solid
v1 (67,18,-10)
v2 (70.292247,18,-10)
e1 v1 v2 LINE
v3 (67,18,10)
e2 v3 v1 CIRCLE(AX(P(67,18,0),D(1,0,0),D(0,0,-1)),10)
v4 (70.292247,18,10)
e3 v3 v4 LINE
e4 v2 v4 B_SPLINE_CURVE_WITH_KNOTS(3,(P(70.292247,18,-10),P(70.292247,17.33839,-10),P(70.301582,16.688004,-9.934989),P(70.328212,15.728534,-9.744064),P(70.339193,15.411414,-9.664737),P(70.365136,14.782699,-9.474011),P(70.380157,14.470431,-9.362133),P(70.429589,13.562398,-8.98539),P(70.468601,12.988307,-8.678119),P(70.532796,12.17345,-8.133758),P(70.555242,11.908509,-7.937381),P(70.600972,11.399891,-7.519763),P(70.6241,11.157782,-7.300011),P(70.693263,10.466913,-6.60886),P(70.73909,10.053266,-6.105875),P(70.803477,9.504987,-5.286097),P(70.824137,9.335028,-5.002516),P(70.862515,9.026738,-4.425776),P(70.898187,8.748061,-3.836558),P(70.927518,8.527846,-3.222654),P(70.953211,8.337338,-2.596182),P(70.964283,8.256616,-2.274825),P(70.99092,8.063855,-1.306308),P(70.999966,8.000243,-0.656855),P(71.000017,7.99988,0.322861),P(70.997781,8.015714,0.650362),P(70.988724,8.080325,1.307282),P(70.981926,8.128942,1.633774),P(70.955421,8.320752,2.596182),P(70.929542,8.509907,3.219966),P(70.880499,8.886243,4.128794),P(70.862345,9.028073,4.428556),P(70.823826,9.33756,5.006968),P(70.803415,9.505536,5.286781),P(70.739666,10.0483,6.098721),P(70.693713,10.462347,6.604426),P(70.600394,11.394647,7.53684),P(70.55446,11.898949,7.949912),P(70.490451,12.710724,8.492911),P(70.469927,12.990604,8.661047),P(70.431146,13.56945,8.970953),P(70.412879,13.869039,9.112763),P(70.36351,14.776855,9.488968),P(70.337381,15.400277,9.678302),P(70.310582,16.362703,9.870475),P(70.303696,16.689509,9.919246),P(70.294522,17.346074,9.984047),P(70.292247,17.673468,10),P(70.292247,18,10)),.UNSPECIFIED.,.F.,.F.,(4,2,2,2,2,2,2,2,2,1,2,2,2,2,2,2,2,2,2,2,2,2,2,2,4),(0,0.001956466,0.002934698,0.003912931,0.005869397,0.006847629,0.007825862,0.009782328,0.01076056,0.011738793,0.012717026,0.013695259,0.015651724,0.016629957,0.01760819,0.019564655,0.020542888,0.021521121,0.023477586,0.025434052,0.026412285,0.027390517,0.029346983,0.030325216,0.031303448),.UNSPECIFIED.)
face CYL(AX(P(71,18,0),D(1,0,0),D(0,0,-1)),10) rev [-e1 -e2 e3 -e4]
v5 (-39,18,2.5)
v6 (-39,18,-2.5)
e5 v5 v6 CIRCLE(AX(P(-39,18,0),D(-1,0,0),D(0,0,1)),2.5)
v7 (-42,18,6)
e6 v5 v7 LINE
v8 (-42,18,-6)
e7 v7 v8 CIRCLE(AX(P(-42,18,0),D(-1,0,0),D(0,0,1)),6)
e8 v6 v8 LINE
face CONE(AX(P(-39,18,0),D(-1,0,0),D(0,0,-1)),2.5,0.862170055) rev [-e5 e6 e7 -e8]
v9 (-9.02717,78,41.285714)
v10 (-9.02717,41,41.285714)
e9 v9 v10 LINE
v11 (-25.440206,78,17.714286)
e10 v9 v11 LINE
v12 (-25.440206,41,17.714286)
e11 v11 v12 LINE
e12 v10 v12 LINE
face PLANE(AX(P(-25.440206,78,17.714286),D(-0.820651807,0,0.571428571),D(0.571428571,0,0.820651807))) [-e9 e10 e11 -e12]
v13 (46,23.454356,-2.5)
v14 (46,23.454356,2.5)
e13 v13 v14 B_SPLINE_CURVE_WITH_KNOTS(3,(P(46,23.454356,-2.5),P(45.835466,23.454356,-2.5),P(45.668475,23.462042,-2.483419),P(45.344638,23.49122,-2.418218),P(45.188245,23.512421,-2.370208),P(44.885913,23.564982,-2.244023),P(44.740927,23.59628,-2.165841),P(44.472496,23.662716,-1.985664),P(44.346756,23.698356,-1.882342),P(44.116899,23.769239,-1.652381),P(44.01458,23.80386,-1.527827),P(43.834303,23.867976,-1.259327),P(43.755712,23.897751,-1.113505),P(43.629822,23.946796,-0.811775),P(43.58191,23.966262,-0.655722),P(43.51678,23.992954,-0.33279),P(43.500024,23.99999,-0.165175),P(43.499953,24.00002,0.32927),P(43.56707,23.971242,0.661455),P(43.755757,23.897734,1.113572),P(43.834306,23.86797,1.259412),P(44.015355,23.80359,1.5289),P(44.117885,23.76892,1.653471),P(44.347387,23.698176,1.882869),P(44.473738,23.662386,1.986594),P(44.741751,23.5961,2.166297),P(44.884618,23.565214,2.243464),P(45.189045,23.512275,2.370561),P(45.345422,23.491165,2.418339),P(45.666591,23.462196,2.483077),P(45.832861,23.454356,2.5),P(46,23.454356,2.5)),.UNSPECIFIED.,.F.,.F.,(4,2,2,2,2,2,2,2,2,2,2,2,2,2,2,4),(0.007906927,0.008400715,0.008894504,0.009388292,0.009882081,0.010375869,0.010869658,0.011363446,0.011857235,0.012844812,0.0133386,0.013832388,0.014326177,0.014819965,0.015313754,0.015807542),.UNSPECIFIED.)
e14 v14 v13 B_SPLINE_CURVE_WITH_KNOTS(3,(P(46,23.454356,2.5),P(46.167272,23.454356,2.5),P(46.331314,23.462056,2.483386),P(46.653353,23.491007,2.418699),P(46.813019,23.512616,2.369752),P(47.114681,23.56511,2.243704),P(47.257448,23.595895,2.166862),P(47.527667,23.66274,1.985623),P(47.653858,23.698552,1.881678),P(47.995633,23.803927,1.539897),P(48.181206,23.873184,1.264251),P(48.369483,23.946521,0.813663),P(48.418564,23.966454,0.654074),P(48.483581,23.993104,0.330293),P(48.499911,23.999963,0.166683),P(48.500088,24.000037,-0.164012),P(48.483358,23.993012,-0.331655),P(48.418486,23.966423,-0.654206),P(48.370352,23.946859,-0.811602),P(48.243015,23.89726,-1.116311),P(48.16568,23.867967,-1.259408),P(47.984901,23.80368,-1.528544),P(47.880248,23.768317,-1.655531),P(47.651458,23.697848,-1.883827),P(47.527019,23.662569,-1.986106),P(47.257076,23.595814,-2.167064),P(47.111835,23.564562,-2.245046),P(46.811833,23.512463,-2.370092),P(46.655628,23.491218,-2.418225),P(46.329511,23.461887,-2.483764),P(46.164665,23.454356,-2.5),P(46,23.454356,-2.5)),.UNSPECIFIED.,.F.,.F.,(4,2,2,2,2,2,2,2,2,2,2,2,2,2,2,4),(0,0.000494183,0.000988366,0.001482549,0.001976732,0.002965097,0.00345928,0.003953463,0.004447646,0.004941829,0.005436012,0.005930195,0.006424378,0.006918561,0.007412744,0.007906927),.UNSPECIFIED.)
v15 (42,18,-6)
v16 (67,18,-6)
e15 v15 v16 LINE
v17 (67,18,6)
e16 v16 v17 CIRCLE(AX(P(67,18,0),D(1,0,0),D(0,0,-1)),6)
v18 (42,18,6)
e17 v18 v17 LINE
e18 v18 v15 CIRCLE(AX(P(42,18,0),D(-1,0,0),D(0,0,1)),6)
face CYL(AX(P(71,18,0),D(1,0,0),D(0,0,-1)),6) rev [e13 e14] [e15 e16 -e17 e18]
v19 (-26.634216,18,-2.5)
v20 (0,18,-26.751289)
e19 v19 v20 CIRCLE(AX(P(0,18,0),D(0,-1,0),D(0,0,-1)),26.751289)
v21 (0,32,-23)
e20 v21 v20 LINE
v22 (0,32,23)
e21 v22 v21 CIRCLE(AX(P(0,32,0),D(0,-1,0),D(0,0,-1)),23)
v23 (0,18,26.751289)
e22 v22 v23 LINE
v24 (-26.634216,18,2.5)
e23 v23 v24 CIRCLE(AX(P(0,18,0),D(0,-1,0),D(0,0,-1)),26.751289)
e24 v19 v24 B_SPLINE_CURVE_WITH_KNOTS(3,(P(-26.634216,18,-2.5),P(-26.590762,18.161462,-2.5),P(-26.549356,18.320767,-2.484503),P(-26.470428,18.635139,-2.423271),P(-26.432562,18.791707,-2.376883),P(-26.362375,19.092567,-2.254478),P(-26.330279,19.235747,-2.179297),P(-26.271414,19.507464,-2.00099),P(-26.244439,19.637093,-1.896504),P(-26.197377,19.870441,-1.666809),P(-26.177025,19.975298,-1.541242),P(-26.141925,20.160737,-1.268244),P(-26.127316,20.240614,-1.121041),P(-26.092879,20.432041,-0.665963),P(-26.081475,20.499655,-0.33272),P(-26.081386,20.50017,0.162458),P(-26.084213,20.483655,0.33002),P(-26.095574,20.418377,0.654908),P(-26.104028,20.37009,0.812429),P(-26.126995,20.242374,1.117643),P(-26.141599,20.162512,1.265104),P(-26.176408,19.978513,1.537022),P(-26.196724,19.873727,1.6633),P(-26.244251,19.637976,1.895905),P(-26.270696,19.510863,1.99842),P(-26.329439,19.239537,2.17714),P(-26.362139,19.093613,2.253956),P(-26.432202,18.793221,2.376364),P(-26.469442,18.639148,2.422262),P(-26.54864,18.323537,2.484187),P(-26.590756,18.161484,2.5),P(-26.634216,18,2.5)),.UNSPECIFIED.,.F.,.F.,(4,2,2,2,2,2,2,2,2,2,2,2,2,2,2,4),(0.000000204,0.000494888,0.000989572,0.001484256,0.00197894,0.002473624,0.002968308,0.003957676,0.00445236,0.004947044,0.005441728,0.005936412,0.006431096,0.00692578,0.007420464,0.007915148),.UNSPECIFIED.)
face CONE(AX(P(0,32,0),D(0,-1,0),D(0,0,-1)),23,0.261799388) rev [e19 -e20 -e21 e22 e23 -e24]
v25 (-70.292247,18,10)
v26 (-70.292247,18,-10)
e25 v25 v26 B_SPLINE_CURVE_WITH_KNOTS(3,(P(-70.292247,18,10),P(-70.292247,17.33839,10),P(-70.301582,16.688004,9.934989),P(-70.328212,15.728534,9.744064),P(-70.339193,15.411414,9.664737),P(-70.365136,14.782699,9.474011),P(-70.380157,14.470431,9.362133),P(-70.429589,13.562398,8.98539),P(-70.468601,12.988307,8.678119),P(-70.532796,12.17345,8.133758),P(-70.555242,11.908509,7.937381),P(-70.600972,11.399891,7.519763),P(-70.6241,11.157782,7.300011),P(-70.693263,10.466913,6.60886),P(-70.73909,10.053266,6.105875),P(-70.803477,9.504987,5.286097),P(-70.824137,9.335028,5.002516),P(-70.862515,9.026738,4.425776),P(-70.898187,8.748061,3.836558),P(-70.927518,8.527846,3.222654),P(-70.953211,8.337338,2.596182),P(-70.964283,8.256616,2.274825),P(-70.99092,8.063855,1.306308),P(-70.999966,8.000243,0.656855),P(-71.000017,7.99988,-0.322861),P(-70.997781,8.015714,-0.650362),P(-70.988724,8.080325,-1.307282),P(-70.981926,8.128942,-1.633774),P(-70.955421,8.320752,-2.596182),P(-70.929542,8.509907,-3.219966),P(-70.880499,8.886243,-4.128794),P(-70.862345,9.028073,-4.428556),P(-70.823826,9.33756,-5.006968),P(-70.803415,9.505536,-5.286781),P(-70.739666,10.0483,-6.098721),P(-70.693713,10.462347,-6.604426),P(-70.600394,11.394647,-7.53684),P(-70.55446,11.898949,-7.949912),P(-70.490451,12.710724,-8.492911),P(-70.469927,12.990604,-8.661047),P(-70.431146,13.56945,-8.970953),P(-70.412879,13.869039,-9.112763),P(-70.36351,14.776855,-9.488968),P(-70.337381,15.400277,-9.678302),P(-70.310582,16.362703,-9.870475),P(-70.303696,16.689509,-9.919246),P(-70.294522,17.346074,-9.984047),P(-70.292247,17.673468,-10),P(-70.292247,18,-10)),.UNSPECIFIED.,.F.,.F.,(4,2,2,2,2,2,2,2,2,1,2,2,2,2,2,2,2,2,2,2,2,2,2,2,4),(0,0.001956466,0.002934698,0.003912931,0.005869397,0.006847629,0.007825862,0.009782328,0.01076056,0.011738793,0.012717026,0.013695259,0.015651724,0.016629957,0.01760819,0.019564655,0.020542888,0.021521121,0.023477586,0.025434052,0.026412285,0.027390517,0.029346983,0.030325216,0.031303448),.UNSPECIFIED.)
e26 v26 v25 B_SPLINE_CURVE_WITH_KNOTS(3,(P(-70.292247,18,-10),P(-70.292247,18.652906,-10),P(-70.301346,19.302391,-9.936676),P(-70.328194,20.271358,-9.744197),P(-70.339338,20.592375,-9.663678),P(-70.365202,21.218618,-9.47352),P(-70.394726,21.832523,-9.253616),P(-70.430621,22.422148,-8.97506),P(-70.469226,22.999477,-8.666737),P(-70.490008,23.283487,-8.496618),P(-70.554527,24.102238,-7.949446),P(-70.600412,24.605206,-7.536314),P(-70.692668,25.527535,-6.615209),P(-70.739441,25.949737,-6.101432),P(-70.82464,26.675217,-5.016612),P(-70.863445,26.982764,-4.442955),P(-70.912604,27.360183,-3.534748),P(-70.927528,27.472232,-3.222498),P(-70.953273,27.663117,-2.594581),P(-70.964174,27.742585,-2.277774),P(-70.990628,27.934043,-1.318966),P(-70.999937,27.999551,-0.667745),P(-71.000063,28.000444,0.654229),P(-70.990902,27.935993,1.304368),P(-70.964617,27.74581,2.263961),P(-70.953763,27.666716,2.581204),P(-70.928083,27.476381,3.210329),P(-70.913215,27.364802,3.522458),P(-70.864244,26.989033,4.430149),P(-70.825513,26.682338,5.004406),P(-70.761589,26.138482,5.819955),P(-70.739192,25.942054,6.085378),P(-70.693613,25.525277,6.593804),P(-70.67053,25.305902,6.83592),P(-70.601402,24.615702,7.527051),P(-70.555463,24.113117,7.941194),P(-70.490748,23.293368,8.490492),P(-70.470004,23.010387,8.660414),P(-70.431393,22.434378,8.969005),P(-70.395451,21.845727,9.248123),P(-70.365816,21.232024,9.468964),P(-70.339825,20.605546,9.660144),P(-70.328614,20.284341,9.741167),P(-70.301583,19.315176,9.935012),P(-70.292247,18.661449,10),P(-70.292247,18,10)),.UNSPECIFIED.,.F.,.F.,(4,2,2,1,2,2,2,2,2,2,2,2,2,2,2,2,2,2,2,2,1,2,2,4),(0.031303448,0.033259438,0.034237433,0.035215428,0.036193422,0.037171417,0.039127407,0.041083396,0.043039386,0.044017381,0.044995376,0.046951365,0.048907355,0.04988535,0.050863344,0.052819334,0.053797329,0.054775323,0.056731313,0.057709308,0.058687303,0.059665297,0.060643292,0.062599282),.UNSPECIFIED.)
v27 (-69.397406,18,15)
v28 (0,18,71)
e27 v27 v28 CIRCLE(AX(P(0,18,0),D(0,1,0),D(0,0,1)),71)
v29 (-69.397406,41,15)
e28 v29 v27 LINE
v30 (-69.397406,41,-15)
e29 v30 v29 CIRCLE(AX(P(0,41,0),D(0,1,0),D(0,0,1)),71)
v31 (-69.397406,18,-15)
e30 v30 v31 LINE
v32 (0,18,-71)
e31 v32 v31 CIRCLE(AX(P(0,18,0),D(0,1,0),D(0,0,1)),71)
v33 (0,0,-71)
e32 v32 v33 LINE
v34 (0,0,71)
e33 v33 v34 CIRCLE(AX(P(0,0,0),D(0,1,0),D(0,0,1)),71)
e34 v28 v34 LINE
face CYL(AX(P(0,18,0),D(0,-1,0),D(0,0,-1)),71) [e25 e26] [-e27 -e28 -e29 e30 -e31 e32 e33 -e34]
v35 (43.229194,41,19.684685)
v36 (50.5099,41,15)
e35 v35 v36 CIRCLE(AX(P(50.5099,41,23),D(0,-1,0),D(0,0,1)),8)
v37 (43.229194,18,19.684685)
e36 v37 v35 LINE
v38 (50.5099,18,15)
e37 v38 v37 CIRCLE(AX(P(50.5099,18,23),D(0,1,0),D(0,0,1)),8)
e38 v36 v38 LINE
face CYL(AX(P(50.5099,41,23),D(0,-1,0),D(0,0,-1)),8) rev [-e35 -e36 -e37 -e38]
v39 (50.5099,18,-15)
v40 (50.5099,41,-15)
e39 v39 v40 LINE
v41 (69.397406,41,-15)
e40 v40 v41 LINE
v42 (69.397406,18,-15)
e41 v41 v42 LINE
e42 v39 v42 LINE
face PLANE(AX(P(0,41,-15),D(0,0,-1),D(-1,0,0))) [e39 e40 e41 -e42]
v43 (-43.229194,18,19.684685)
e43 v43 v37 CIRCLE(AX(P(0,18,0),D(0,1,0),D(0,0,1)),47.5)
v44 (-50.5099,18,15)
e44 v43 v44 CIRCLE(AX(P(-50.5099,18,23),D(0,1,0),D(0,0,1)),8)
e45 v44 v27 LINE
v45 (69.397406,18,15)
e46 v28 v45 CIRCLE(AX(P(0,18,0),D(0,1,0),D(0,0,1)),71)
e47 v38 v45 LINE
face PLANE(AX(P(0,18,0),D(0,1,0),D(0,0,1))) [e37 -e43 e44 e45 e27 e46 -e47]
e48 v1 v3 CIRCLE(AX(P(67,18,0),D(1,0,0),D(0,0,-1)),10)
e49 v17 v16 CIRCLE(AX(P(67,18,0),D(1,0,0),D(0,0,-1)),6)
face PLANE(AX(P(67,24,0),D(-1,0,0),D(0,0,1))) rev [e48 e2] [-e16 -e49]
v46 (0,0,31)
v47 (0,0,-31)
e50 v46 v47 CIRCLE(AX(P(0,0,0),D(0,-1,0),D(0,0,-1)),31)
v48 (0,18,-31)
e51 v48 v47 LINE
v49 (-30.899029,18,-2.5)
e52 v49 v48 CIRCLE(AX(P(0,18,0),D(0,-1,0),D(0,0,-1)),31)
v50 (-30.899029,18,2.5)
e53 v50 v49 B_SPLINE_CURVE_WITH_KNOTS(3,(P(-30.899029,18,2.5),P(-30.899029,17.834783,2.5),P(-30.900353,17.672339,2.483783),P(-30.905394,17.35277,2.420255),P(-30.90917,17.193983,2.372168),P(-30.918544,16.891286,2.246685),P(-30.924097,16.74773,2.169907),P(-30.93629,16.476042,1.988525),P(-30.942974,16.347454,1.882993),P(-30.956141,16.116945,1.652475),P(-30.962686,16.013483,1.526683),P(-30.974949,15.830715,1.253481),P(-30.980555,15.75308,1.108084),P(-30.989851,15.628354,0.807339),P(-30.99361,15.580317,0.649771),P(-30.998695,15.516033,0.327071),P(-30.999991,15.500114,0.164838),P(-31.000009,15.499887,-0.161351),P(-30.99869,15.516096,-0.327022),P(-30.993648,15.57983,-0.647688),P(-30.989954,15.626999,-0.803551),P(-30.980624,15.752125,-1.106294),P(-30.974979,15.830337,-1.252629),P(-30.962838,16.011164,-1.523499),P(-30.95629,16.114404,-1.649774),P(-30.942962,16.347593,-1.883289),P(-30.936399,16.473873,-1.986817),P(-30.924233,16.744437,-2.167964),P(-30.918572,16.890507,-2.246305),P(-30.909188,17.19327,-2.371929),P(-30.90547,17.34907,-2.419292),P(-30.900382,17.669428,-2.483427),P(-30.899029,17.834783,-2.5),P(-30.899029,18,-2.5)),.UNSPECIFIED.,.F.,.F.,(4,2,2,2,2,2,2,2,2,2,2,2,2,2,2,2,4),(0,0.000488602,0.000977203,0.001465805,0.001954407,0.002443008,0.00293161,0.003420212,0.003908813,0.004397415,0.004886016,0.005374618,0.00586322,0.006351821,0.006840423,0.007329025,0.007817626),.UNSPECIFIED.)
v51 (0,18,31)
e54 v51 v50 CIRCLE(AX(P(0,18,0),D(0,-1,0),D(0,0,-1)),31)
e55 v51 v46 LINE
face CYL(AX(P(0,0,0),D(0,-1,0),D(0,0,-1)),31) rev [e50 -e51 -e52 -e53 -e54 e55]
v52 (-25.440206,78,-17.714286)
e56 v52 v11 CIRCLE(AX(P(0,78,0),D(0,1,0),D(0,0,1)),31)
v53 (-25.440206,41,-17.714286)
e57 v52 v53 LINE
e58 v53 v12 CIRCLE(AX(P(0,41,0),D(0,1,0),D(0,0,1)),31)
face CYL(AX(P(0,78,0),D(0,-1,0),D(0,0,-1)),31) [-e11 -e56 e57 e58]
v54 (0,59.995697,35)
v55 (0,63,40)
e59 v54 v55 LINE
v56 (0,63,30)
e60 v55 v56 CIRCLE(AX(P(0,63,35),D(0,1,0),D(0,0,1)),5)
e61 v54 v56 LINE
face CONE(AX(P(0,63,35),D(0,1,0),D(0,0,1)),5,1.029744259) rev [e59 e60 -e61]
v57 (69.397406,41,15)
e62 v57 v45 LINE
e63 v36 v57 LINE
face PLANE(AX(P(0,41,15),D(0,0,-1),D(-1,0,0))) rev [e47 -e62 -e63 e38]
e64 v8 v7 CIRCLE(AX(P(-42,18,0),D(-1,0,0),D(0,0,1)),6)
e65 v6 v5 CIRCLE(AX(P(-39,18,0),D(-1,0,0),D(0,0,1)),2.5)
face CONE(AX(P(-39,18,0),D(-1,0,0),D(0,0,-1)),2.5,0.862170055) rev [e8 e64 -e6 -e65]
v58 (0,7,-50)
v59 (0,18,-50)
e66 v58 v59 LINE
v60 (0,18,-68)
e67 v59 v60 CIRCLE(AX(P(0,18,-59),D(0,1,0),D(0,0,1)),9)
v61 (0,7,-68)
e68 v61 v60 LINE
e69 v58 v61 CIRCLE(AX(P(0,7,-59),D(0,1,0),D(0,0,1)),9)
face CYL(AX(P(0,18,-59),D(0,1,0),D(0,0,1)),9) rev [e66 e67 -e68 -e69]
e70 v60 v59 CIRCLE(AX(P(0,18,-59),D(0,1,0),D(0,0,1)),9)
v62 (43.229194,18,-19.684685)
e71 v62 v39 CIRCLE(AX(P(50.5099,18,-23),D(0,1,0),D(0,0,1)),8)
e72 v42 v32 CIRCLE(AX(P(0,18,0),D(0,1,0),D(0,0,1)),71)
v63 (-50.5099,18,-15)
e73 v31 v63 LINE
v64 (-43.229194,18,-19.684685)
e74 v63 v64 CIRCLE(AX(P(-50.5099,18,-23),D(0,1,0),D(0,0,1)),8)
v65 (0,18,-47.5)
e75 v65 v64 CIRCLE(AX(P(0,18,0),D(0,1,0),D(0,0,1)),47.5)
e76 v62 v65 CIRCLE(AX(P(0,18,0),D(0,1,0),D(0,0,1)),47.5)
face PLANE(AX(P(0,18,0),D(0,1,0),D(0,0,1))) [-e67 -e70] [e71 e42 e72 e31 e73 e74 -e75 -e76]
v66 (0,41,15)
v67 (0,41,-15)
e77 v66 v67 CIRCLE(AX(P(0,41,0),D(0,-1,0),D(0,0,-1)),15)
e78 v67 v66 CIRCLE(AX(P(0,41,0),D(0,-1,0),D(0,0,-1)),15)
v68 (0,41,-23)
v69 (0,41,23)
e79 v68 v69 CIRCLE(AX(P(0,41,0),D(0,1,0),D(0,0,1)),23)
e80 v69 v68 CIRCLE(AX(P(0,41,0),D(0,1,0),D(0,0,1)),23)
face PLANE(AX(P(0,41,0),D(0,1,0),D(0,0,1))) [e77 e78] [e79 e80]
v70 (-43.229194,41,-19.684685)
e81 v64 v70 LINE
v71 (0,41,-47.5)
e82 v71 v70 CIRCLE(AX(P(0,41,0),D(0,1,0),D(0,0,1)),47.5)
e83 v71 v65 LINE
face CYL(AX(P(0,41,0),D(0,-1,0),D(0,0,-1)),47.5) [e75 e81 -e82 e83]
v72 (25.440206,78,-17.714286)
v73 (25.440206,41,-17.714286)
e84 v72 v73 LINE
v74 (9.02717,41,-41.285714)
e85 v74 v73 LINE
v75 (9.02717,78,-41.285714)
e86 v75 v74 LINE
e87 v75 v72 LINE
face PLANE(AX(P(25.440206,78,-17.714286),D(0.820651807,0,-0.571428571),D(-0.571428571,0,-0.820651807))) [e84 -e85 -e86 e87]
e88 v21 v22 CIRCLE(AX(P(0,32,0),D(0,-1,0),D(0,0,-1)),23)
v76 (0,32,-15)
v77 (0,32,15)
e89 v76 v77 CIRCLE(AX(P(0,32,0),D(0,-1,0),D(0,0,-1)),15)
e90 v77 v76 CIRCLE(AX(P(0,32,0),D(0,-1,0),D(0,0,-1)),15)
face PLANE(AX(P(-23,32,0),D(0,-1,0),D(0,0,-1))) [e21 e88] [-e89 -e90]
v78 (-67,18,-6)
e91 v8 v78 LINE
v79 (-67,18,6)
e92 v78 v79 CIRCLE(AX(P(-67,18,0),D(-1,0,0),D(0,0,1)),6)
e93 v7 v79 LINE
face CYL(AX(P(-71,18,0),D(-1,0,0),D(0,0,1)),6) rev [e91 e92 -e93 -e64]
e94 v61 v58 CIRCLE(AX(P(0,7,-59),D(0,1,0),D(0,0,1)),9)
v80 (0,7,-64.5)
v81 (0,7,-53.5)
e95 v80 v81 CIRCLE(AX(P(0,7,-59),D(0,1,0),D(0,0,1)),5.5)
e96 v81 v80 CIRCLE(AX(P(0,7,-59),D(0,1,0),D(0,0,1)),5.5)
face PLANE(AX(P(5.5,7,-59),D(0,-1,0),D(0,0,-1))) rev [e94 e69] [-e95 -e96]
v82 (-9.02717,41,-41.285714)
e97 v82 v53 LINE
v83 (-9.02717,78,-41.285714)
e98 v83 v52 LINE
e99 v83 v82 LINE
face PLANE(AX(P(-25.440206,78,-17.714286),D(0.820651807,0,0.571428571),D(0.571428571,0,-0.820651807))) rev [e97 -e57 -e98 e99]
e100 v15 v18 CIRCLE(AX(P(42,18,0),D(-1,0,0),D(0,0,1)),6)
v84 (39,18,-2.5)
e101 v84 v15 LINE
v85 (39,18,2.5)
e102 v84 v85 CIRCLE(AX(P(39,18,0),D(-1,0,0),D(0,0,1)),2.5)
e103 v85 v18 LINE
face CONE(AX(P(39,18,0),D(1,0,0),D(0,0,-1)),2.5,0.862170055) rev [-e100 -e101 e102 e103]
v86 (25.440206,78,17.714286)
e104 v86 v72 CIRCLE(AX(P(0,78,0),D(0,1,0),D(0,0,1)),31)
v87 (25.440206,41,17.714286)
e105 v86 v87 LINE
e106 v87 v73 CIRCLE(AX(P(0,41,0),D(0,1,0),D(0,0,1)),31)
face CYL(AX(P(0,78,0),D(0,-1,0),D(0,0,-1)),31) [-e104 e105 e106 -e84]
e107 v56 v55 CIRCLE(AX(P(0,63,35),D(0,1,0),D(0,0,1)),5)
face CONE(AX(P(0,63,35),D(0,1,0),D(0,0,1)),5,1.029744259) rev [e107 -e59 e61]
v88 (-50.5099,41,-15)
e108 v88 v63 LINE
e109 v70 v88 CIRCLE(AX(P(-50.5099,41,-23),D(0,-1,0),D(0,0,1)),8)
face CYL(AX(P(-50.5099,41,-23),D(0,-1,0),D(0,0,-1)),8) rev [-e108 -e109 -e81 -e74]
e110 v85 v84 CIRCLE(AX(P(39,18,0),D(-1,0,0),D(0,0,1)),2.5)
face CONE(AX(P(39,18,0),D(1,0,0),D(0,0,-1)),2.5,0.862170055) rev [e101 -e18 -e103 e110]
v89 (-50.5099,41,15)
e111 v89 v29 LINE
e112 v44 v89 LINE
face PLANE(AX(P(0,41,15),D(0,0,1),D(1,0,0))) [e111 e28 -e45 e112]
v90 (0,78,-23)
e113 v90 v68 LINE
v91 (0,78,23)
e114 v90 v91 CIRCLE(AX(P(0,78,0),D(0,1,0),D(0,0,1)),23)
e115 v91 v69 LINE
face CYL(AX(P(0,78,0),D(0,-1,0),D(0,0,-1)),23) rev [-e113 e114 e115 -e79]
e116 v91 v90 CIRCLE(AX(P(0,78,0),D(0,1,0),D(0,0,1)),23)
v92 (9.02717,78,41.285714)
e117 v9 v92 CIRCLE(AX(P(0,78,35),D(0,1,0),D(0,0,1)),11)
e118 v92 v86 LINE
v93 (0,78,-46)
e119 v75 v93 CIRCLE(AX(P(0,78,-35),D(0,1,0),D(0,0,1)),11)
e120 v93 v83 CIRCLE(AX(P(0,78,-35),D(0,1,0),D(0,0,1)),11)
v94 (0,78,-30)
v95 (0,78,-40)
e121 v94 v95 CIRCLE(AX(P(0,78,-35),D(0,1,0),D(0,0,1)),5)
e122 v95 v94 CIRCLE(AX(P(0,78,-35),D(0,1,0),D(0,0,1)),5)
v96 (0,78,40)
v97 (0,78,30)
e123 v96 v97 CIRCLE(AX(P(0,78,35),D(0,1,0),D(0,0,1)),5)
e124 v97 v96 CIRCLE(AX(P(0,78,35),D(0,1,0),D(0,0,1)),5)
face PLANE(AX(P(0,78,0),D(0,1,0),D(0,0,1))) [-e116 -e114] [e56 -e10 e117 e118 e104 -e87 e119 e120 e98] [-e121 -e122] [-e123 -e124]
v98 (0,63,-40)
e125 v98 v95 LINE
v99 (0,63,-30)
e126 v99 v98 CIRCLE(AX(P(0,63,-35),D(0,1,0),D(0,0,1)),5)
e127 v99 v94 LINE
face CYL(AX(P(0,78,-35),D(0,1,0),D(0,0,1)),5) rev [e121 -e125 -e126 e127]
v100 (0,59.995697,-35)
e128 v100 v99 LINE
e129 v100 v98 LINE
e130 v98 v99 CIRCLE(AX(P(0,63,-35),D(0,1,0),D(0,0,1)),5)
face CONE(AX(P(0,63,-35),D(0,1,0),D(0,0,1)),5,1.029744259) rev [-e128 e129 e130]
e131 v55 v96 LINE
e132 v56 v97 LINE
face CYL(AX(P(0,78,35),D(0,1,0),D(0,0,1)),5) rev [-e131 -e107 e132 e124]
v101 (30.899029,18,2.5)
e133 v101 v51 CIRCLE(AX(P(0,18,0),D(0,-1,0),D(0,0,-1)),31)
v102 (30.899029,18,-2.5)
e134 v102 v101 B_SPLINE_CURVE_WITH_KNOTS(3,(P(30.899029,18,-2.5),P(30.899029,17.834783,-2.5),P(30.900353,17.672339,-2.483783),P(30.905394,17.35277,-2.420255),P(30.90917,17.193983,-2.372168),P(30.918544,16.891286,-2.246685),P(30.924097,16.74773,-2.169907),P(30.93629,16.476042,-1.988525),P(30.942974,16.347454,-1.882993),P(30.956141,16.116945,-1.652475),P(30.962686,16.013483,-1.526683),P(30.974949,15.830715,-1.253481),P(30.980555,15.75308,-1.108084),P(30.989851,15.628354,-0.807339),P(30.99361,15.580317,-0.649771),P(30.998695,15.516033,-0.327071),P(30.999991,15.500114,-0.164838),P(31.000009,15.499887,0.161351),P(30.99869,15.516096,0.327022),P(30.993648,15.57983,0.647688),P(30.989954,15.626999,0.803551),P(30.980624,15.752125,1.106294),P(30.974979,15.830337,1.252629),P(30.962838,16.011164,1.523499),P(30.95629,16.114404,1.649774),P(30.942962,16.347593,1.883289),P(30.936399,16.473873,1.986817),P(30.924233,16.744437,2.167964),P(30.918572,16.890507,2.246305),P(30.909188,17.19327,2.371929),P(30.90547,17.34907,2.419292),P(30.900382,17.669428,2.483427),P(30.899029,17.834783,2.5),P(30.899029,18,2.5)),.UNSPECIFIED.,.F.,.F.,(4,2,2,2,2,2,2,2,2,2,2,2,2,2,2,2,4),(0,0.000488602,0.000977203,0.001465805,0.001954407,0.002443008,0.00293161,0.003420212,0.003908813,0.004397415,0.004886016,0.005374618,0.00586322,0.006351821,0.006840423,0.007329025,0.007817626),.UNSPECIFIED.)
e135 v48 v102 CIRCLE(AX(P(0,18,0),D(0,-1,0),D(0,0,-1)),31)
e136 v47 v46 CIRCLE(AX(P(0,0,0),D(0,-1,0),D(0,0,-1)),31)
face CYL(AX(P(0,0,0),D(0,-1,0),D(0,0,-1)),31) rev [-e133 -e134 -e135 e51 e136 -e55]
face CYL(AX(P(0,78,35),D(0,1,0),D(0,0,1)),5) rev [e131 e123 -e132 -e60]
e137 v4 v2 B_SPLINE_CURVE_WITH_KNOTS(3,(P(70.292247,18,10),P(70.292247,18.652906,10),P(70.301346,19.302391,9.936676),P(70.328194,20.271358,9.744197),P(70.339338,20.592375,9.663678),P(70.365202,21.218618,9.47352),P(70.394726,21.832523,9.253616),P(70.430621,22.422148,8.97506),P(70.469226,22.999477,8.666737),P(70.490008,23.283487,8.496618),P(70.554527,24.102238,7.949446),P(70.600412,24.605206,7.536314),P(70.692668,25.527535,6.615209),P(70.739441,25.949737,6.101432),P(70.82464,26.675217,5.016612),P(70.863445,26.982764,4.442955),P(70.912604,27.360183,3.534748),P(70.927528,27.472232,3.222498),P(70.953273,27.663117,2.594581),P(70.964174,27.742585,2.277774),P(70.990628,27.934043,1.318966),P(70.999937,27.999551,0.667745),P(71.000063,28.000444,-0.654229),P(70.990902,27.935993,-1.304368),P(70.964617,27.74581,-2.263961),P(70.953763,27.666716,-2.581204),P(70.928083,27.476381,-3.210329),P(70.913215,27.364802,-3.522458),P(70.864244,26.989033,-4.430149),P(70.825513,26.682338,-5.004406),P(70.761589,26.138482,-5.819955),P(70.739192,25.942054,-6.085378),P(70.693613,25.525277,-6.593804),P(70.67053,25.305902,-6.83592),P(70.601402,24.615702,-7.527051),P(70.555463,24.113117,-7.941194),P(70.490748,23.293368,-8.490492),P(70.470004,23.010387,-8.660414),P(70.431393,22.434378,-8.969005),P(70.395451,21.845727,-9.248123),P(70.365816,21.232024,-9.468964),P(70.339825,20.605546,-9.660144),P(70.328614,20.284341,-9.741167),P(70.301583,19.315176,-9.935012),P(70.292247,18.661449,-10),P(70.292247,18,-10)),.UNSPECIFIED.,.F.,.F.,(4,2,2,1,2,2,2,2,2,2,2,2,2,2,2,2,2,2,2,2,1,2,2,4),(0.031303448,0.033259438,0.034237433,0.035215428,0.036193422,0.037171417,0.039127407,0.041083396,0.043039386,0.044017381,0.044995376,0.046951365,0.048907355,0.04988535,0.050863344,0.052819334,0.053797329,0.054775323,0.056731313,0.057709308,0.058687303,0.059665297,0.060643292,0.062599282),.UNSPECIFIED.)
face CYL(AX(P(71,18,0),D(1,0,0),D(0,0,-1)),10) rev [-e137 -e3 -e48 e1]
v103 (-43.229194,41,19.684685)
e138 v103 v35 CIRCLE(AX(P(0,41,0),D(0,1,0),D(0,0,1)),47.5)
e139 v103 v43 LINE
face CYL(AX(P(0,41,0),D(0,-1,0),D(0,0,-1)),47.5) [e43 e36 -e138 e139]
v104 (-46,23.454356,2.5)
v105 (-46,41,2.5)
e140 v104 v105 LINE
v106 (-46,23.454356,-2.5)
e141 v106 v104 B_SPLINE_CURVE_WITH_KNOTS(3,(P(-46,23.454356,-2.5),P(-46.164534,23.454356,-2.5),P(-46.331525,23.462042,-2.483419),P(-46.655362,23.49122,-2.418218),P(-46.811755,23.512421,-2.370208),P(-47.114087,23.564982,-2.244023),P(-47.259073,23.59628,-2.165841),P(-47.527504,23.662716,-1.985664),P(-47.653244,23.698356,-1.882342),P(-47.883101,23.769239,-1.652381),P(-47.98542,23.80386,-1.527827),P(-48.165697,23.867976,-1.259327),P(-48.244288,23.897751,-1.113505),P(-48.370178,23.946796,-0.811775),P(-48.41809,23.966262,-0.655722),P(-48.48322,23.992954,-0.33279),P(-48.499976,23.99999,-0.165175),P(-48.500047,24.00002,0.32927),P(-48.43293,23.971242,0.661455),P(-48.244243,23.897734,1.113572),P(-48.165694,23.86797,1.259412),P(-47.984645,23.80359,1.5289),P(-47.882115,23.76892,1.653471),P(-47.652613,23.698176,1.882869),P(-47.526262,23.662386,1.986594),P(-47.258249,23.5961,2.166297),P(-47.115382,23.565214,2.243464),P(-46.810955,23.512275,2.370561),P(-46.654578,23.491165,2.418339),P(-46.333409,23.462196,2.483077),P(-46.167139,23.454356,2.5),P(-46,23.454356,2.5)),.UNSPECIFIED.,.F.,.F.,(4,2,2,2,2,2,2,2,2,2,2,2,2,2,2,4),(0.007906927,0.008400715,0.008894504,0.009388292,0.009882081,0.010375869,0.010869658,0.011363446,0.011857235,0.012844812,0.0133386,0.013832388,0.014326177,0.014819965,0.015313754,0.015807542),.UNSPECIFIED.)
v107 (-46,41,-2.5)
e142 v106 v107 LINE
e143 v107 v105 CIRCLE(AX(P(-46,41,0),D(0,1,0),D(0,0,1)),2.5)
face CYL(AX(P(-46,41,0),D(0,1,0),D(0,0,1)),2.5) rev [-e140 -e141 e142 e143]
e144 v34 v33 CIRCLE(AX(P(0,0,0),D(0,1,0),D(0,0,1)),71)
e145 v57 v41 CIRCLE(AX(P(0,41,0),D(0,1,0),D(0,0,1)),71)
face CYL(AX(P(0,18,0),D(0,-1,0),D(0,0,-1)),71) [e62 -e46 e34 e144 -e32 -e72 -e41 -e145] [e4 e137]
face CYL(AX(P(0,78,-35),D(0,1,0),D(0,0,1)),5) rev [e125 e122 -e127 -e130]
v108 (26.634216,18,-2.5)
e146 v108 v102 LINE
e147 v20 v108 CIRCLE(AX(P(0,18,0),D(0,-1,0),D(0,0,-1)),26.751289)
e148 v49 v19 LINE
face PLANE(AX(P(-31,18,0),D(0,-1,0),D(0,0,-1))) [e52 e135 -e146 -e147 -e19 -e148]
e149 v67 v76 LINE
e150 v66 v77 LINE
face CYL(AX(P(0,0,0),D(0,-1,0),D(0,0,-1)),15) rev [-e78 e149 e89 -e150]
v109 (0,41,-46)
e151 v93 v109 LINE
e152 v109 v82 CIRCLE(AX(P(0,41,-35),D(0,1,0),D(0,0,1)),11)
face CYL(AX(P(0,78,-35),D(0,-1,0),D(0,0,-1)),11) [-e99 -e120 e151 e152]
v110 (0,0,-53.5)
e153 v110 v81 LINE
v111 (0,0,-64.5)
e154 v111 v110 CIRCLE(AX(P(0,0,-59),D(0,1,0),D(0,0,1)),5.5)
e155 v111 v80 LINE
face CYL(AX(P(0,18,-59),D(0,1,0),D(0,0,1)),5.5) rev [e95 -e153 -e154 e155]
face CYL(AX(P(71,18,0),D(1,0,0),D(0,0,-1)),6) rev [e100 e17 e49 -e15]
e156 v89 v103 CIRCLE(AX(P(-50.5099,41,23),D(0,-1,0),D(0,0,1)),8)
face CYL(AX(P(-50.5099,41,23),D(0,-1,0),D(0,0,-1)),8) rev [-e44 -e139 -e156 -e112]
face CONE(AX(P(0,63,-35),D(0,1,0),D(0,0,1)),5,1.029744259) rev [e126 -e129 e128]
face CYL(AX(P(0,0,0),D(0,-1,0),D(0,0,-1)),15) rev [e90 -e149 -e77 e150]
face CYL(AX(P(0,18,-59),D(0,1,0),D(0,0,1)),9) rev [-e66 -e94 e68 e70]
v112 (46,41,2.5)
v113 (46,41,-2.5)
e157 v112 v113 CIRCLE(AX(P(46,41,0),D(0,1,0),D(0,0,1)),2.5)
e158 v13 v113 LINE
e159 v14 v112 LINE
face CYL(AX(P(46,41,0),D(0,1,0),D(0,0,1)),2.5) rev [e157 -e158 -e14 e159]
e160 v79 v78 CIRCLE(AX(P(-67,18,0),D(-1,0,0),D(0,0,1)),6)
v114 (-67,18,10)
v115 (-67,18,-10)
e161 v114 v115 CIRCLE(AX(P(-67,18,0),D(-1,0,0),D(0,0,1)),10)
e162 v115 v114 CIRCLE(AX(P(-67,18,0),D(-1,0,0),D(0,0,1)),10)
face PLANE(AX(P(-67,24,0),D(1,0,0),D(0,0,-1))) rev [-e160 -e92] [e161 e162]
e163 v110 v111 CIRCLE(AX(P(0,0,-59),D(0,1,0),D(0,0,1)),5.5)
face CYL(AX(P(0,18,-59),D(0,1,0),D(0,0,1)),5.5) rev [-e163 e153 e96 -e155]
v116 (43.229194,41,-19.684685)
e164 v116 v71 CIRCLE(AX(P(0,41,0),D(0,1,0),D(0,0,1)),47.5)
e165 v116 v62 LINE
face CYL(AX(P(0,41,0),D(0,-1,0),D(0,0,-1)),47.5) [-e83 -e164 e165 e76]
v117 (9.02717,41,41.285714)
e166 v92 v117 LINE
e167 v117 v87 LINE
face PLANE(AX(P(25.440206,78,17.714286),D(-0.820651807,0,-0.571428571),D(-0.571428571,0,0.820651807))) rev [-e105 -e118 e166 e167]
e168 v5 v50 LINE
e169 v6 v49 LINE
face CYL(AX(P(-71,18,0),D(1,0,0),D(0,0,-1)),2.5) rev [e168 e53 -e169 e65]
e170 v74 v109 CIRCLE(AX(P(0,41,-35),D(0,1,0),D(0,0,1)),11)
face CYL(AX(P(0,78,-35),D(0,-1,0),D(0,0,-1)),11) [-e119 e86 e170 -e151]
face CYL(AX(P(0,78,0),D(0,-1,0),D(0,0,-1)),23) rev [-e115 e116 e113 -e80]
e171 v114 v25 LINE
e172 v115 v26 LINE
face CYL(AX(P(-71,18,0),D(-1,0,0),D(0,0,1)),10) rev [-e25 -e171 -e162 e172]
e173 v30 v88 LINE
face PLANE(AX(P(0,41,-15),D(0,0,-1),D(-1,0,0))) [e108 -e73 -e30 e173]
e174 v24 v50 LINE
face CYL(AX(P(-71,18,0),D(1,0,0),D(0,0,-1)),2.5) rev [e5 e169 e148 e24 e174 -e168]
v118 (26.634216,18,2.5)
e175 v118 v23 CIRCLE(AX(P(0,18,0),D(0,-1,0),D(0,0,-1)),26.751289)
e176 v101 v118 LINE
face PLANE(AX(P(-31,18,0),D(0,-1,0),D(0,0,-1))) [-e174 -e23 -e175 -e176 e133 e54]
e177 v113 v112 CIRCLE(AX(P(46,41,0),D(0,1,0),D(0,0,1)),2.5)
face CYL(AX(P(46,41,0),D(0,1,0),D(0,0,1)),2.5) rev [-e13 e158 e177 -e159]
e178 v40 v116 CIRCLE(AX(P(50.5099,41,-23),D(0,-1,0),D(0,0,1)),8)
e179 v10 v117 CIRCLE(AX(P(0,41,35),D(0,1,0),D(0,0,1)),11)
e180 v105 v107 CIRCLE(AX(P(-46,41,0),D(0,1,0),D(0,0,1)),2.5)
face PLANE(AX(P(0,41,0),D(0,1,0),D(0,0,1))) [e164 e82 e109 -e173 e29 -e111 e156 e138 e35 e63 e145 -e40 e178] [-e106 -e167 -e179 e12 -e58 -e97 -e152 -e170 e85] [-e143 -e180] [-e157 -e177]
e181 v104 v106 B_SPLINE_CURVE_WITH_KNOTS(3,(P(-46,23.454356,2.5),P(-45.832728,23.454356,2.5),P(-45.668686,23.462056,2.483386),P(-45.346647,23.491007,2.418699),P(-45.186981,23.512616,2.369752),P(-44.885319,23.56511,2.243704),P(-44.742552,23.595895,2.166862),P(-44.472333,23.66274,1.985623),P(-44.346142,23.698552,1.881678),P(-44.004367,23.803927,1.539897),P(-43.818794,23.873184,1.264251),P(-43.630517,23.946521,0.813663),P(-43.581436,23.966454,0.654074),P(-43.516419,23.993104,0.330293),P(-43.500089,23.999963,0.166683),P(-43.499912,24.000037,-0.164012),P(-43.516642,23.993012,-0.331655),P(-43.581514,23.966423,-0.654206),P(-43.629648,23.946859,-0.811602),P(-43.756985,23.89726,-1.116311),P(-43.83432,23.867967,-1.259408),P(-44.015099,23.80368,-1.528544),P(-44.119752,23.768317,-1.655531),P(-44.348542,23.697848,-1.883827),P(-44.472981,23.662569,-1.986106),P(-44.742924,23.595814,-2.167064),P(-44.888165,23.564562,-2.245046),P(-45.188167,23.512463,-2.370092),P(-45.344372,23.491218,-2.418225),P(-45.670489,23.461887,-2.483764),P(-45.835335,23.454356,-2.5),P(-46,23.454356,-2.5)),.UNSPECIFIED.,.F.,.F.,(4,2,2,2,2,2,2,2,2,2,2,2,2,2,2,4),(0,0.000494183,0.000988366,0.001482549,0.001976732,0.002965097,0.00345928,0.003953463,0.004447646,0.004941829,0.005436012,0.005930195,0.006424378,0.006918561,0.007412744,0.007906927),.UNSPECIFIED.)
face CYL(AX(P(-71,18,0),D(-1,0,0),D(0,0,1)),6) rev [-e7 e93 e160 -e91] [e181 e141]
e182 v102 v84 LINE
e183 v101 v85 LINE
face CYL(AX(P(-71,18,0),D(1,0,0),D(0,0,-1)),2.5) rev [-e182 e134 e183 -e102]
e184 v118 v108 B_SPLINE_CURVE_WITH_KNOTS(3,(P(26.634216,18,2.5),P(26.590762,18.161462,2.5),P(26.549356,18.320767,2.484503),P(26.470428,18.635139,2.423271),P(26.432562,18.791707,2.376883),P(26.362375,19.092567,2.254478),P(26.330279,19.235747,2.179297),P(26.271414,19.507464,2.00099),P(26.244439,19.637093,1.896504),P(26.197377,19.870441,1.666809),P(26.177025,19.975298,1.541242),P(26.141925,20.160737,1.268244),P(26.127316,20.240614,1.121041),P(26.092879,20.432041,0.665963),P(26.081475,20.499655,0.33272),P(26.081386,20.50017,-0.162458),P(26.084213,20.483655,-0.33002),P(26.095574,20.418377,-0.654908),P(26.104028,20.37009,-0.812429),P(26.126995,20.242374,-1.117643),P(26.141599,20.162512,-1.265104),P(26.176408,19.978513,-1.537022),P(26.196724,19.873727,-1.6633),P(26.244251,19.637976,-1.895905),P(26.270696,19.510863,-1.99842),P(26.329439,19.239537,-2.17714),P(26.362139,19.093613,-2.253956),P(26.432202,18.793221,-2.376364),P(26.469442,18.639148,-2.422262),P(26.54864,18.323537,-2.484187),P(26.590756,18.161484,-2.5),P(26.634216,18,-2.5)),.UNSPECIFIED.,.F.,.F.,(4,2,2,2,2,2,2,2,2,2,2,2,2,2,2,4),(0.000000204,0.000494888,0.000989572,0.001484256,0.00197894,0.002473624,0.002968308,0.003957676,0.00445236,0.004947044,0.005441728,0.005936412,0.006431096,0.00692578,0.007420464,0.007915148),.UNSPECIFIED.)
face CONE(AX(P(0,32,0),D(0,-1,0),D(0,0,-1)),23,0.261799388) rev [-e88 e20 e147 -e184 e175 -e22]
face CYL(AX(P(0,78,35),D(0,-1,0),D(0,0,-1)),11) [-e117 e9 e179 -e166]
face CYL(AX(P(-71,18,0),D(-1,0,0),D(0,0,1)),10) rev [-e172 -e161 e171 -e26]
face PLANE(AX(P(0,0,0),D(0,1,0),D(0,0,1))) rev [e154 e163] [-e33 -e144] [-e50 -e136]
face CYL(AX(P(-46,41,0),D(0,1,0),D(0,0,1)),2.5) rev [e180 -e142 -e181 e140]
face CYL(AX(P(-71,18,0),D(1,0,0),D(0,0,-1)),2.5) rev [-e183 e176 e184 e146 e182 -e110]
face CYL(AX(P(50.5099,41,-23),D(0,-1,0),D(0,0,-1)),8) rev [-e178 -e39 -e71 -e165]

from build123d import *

# Parameters (mm, degrees)
HOUSING_PROFILE_SKETCH_R              = 71
MOUNTING_FLANGE_142_DEPTH             = 18
BODY_START                            = 18
BODY_BOSS_WITH_SIDE_LUGS_DEPTH        = 23
UPPER_START                           = 41
SKETCH1_5_R                           = 23
UPPER_BEARING_BOSS_DEPTH              = 37
BOSS_FILLET_R8_R                      = 8
FLANGE_HOLES_6X_11_C_BORE_D           = 11
FLANGE_HOLES_6X_11_C_BORE_CBORE_D     = 18
FLANGE_HOLES_6X_11_C_BORE_CBORE_DEPTH = 11
SIDE_PORT_12_C_BORE_D                 = 12
SIDE_PORT_12_C_BORE_DEPTH             = 29
SIDE_PORT_12_C_BORE_CBORE_D           = 20
SIDE_PORT_12_C_BORE_CBORE_DEPTH       = 4
SIDE_PORT_RELIEF_CUT_DEPTH            = 128.145585958
SIDE_PORT_RELIEF_CUT_DEPTH_BACK       = 128.145585958
SIDE_PORT_RELIEF_SKETCH_R             = 2.5
UPPER_BOSS_HOLES_10_D                 = 10
UPPER_BOSS_HOLES_10_DEPTH             = 15
UPPER_BOSS_HOLES_10_TIP               = 3.004303095
LUBE_HOLE_5_REACH                     = 110.457
LUBE_HOLE_5_BORE_R                    = 2.5


with BuildPart() as part:
    # Housing Profile Sketch → Mounting Flange _142 (new body)
    with BuildSketch(Plane(origin=(0, 0, 0), x_dir=(1, 0, 0), z_dir=(0, 1, 0))):
        with Locations(Location((0, 0, 0), (0, 0, 270))):
            Circle(HOUSING_PROFILE_SKETCH_R)
    extrude(amount=MOUNTING_FLANGE_142_DEPTH)

    # Sketch1_3 → Body Boss with Side Lugs (add)
    with BuildSketch(Plane(origin=(0, 0, 0), x_dir=(1, 0, 0), z_dir=(0, 1, 0)).offset(BODY_START)):
        with BuildLine():
            ThreePointArc((45.069390943, 15), (0, 47.5), (-45.069390943, 15))
            Line((-45.069390943, 15), (-69.397406292, 15))
            ThreePointArc((-69.397406292, 15), (-71, 0), (-69.397406292, -15))
            Line((-69.397406292, -15), (-45.069390943, -15))
            ThreePointArc((-45.069390943, -15), (0, -47.5), (45.069390943, -15))
            Line((45.069390943, -15), (69.397406292, -15))
            ThreePointArc((69.397406292, -15), (71, 0), (69.397406292, 15))
            Line((69.397406292, 15), (45.069390943, 15))
        make_face()
    extrude(amount=BODY_BOSS_WITH_SIDE_LUGS_DEPTH)

    # Sketch1_5 → Upper Bearing Boss (add)
    with BuildSketch(Plane(origin=(0, 0, 0), x_dir=(1, 0, 0), z_dir=(0, 1, 0)).offset(UPPER_START)):
        with BuildLine():
            Line((25.440206006, -17.714285714), (9.027169873, -41.285714286))
            ThreePointArc((9.027169873, -41.285714286), (0, -46), (-9.027169873, -41.285714286))
            Line((-9.027169873, -41.285714286), (-25.440206006, -17.714285714))
            ThreePointArc((-25.440206006, -17.714285714), (-31, 0), (-25.440206006, 17.714285714))
            Line((-25.440206006, 17.714285714), (-9.027169873, 41.285714286))
            ThreePointArc((-9.027169873, 41.285714286), (0, 46), (9.027169873, 41.285714286))
            Line((9.027169873, 41.285714286), (25.440206006, 17.714285714))
            ThreePointArc((25.440206006, 17.714285714), (31, 0), (25.440206006, -17.714285714))
        make_face()
        with Locations(Location((0, 0, 0), (0, 0, 270))):
            Circle(SKETCH1_5_R, mode=Mode.SUBTRACT)
    extrude(amount=UPPER_BEARING_BOSS_DEPTH)

    # Boss Fillet R8
    boss_fillet_r8_edges = [part.edges().sort_by_distance(p)[0] for p in [
        (45.069390943, 29.5, -15),
        (-45.069390943, 29.5, -15),
        (-45.069390943, 29.5, 15),
        (45.069390943, 29.5, 15),
    ]]
    fillet(boss_fillet_r8_edges, radius=BOSS_FILLET_R8_R)

    # Flange Holes 6x_11 C-Bore (through all)
    with Locations(Plane(origin=(0, 18, 0), x_dir=(1, 0, 0), z_dir=(0, 1, 0))):
        with Locations((0, 59)):
            CounterBoreHole(FLANGE_HOLES_6X_11_C_BORE_D / 2, FLANGE_HOLES_6X_11_C_BORE_CBORE_D / 2, FLANGE_HOLES_6X_11_C_BORE_CBORE_DEPTH)

    # Bearing Bore Profile → Bearing Bore (revolve, cut)
    with BuildSketch(Plane.XY, mode=Mode.PRIVATE) as bearing_bore_sk:
        Polygon((-31, 0), (-31, 18), (-26.751288694, 18), (-23, 32), (-15, 32), (-15, 41), (0, 41), (0, 0), align=None)
    revolve(bearing_bore_sk.sketch.rotate(Axis((0, 0, 0), (0, 1, 0)), 270), axis=Axis((0, 0, 0), (0, 1, 0)), mode=Mode.SUBTRACT)

    # Side Port _12 C-Bore
    with Locations(Plane(origin=(71, 18, 0), x_dir=(0, 0, 1), z_dir=(1, 0, 0))):
        with Locations((0, 0)):
            side_port_12_c_bore = CounterBoreHole(SIDE_PORT_12_C_BORE_D / 2, SIDE_PORT_12_C_BORE_CBORE_D / 2, SIDE_PORT_12_C_BORE_CBORE_DEPTH, depth=SIDE_PORT_12_C_BORE_DEPTH)

    # Side Port Relief Sketch → Side Port Relief Cut (cut, two sides: drawn at the far end of the back side and taken through both)
    with BuildSketch(Plane(origin=(0, 0, 0), x_dir=(0, 0, -1), z_dir=(1, 0, 0)).offset(-SIDE_PORT_RELIEF_CUT_DEPTH_BACK)):
        with Locations(Location((0, 18, 0), (0, 0, 180))):
            Circle(SIDE_PORT_RELIEF_SKETCH_R)
    extrude(amount=SIDE_PORT_RELIEF_CUT_DEPTH + SIDE_PORT_RELIEF_CUT_DEPTH_BACK, mode=Mode.SUBTRACT)

    # Side Port Groove Profile → Side Port Groove (revolve, cut)
    with BuildSketch(Plane.XY, mode=Mode.PRIVATE) as side_port_groove_sk:
        Polygon((42, 12), (39, 15.5), (39, 18), (42, 18), align=None)
    side_port_groove = revolve(side_port_groove_sk.sketch.rotate(Axis((39, 18, 0), (1, 0, 0)), 90), axis=Axis((39, 18, 0), (1, 0, 0)), mode=Mode.SUBTRACT)

    # Side Port Mirror: Side Port _12 C-Bore, Side Port Groove across plane
    add(side_port_12_c_bore.mirror(Plane(origin=(0, 0, 0), x_dir=(0, 0, 1), z_dir=(1, 0, 0))), mode=Mode.SUBTRACT)
    add(side_port_groove.mirror(Plane(origin=(0, 0, 0), x_dir=(0, 0, 1), z_dir=(1, 0, 0))), mode=Mode.SUBTRACT)

    # Upper Boss Holes _10
    with Locations(Plane(origin=(0, 78, 0), x_dir=(1, 0, 0), z_dir=(0, 1, 0))):
        with Locations((0, 35), (0, -35)):
            Hole(UPPER_BOSS_HOLES_10_D / 2, depth=UPPER_BOSS_HOLES_10_DEPTH)
            with Locations((0, 0, -(UPPER_BOSS_HOLES_10_DEPTH + UPPER_BOSS_HOLES_10_TIP / 2))):  # 118° drill point
                Cone(0, UPPER_BOSS_HOLES_10_D / 2, UPPER_BOSS_HOLES_10_TIP, mode=Mode.SUBTRACT)

    # Lube Hole _5 bore → Lube Hole _5 (cut, up to next)
    with BuildSketch(Plane(origin=(0, 41, 0), x_dir=(1, 0, 0), z_dir=(0, 1, 0)), mode=Mode.PRIVATE) as lube_hole_5_sk1:
        with Locations((46, 0)):
            Circle(LUBE_HOLE_5_BORE_R)
    lube_hole_5_tool1 = extrude(lube_hole_5_sk1.sketch, amount=-LUBE_HOLE_5_REACH, mode=Mode.PRIVATE) & part.part
    # Lube Hole _5 bore → Lube Hole _5 (cut, up to next)
    with BuildSketch(Plane(origin=(0, 41, 0), x_dir=(1, 0, 0), z_dir=(0, 1, 0)), mode=Mode.PRIVATE) as lube_hole_5_sk2:
        with Locations((-46, 0)):
            Circle(LUBE_HOLE_5_BORE_R)
    lube_hole_5_tool2 = extrude(lube_hole_5_sk2.sketch, amount=-LUBE_HOLE_5_REACH, mode=Mode.PRIVATE) & part.part
    add(lube_hole_5_tool1.solids().sort_by_distance((46, 41, 0))[0], mode=Mode.SUBTRACT)
    add(lube_hole_5_tool2.solids().sort_by_distance((-46, 41, 0))[0], mode=Mode.SUBTRACT)


solid = part.part
